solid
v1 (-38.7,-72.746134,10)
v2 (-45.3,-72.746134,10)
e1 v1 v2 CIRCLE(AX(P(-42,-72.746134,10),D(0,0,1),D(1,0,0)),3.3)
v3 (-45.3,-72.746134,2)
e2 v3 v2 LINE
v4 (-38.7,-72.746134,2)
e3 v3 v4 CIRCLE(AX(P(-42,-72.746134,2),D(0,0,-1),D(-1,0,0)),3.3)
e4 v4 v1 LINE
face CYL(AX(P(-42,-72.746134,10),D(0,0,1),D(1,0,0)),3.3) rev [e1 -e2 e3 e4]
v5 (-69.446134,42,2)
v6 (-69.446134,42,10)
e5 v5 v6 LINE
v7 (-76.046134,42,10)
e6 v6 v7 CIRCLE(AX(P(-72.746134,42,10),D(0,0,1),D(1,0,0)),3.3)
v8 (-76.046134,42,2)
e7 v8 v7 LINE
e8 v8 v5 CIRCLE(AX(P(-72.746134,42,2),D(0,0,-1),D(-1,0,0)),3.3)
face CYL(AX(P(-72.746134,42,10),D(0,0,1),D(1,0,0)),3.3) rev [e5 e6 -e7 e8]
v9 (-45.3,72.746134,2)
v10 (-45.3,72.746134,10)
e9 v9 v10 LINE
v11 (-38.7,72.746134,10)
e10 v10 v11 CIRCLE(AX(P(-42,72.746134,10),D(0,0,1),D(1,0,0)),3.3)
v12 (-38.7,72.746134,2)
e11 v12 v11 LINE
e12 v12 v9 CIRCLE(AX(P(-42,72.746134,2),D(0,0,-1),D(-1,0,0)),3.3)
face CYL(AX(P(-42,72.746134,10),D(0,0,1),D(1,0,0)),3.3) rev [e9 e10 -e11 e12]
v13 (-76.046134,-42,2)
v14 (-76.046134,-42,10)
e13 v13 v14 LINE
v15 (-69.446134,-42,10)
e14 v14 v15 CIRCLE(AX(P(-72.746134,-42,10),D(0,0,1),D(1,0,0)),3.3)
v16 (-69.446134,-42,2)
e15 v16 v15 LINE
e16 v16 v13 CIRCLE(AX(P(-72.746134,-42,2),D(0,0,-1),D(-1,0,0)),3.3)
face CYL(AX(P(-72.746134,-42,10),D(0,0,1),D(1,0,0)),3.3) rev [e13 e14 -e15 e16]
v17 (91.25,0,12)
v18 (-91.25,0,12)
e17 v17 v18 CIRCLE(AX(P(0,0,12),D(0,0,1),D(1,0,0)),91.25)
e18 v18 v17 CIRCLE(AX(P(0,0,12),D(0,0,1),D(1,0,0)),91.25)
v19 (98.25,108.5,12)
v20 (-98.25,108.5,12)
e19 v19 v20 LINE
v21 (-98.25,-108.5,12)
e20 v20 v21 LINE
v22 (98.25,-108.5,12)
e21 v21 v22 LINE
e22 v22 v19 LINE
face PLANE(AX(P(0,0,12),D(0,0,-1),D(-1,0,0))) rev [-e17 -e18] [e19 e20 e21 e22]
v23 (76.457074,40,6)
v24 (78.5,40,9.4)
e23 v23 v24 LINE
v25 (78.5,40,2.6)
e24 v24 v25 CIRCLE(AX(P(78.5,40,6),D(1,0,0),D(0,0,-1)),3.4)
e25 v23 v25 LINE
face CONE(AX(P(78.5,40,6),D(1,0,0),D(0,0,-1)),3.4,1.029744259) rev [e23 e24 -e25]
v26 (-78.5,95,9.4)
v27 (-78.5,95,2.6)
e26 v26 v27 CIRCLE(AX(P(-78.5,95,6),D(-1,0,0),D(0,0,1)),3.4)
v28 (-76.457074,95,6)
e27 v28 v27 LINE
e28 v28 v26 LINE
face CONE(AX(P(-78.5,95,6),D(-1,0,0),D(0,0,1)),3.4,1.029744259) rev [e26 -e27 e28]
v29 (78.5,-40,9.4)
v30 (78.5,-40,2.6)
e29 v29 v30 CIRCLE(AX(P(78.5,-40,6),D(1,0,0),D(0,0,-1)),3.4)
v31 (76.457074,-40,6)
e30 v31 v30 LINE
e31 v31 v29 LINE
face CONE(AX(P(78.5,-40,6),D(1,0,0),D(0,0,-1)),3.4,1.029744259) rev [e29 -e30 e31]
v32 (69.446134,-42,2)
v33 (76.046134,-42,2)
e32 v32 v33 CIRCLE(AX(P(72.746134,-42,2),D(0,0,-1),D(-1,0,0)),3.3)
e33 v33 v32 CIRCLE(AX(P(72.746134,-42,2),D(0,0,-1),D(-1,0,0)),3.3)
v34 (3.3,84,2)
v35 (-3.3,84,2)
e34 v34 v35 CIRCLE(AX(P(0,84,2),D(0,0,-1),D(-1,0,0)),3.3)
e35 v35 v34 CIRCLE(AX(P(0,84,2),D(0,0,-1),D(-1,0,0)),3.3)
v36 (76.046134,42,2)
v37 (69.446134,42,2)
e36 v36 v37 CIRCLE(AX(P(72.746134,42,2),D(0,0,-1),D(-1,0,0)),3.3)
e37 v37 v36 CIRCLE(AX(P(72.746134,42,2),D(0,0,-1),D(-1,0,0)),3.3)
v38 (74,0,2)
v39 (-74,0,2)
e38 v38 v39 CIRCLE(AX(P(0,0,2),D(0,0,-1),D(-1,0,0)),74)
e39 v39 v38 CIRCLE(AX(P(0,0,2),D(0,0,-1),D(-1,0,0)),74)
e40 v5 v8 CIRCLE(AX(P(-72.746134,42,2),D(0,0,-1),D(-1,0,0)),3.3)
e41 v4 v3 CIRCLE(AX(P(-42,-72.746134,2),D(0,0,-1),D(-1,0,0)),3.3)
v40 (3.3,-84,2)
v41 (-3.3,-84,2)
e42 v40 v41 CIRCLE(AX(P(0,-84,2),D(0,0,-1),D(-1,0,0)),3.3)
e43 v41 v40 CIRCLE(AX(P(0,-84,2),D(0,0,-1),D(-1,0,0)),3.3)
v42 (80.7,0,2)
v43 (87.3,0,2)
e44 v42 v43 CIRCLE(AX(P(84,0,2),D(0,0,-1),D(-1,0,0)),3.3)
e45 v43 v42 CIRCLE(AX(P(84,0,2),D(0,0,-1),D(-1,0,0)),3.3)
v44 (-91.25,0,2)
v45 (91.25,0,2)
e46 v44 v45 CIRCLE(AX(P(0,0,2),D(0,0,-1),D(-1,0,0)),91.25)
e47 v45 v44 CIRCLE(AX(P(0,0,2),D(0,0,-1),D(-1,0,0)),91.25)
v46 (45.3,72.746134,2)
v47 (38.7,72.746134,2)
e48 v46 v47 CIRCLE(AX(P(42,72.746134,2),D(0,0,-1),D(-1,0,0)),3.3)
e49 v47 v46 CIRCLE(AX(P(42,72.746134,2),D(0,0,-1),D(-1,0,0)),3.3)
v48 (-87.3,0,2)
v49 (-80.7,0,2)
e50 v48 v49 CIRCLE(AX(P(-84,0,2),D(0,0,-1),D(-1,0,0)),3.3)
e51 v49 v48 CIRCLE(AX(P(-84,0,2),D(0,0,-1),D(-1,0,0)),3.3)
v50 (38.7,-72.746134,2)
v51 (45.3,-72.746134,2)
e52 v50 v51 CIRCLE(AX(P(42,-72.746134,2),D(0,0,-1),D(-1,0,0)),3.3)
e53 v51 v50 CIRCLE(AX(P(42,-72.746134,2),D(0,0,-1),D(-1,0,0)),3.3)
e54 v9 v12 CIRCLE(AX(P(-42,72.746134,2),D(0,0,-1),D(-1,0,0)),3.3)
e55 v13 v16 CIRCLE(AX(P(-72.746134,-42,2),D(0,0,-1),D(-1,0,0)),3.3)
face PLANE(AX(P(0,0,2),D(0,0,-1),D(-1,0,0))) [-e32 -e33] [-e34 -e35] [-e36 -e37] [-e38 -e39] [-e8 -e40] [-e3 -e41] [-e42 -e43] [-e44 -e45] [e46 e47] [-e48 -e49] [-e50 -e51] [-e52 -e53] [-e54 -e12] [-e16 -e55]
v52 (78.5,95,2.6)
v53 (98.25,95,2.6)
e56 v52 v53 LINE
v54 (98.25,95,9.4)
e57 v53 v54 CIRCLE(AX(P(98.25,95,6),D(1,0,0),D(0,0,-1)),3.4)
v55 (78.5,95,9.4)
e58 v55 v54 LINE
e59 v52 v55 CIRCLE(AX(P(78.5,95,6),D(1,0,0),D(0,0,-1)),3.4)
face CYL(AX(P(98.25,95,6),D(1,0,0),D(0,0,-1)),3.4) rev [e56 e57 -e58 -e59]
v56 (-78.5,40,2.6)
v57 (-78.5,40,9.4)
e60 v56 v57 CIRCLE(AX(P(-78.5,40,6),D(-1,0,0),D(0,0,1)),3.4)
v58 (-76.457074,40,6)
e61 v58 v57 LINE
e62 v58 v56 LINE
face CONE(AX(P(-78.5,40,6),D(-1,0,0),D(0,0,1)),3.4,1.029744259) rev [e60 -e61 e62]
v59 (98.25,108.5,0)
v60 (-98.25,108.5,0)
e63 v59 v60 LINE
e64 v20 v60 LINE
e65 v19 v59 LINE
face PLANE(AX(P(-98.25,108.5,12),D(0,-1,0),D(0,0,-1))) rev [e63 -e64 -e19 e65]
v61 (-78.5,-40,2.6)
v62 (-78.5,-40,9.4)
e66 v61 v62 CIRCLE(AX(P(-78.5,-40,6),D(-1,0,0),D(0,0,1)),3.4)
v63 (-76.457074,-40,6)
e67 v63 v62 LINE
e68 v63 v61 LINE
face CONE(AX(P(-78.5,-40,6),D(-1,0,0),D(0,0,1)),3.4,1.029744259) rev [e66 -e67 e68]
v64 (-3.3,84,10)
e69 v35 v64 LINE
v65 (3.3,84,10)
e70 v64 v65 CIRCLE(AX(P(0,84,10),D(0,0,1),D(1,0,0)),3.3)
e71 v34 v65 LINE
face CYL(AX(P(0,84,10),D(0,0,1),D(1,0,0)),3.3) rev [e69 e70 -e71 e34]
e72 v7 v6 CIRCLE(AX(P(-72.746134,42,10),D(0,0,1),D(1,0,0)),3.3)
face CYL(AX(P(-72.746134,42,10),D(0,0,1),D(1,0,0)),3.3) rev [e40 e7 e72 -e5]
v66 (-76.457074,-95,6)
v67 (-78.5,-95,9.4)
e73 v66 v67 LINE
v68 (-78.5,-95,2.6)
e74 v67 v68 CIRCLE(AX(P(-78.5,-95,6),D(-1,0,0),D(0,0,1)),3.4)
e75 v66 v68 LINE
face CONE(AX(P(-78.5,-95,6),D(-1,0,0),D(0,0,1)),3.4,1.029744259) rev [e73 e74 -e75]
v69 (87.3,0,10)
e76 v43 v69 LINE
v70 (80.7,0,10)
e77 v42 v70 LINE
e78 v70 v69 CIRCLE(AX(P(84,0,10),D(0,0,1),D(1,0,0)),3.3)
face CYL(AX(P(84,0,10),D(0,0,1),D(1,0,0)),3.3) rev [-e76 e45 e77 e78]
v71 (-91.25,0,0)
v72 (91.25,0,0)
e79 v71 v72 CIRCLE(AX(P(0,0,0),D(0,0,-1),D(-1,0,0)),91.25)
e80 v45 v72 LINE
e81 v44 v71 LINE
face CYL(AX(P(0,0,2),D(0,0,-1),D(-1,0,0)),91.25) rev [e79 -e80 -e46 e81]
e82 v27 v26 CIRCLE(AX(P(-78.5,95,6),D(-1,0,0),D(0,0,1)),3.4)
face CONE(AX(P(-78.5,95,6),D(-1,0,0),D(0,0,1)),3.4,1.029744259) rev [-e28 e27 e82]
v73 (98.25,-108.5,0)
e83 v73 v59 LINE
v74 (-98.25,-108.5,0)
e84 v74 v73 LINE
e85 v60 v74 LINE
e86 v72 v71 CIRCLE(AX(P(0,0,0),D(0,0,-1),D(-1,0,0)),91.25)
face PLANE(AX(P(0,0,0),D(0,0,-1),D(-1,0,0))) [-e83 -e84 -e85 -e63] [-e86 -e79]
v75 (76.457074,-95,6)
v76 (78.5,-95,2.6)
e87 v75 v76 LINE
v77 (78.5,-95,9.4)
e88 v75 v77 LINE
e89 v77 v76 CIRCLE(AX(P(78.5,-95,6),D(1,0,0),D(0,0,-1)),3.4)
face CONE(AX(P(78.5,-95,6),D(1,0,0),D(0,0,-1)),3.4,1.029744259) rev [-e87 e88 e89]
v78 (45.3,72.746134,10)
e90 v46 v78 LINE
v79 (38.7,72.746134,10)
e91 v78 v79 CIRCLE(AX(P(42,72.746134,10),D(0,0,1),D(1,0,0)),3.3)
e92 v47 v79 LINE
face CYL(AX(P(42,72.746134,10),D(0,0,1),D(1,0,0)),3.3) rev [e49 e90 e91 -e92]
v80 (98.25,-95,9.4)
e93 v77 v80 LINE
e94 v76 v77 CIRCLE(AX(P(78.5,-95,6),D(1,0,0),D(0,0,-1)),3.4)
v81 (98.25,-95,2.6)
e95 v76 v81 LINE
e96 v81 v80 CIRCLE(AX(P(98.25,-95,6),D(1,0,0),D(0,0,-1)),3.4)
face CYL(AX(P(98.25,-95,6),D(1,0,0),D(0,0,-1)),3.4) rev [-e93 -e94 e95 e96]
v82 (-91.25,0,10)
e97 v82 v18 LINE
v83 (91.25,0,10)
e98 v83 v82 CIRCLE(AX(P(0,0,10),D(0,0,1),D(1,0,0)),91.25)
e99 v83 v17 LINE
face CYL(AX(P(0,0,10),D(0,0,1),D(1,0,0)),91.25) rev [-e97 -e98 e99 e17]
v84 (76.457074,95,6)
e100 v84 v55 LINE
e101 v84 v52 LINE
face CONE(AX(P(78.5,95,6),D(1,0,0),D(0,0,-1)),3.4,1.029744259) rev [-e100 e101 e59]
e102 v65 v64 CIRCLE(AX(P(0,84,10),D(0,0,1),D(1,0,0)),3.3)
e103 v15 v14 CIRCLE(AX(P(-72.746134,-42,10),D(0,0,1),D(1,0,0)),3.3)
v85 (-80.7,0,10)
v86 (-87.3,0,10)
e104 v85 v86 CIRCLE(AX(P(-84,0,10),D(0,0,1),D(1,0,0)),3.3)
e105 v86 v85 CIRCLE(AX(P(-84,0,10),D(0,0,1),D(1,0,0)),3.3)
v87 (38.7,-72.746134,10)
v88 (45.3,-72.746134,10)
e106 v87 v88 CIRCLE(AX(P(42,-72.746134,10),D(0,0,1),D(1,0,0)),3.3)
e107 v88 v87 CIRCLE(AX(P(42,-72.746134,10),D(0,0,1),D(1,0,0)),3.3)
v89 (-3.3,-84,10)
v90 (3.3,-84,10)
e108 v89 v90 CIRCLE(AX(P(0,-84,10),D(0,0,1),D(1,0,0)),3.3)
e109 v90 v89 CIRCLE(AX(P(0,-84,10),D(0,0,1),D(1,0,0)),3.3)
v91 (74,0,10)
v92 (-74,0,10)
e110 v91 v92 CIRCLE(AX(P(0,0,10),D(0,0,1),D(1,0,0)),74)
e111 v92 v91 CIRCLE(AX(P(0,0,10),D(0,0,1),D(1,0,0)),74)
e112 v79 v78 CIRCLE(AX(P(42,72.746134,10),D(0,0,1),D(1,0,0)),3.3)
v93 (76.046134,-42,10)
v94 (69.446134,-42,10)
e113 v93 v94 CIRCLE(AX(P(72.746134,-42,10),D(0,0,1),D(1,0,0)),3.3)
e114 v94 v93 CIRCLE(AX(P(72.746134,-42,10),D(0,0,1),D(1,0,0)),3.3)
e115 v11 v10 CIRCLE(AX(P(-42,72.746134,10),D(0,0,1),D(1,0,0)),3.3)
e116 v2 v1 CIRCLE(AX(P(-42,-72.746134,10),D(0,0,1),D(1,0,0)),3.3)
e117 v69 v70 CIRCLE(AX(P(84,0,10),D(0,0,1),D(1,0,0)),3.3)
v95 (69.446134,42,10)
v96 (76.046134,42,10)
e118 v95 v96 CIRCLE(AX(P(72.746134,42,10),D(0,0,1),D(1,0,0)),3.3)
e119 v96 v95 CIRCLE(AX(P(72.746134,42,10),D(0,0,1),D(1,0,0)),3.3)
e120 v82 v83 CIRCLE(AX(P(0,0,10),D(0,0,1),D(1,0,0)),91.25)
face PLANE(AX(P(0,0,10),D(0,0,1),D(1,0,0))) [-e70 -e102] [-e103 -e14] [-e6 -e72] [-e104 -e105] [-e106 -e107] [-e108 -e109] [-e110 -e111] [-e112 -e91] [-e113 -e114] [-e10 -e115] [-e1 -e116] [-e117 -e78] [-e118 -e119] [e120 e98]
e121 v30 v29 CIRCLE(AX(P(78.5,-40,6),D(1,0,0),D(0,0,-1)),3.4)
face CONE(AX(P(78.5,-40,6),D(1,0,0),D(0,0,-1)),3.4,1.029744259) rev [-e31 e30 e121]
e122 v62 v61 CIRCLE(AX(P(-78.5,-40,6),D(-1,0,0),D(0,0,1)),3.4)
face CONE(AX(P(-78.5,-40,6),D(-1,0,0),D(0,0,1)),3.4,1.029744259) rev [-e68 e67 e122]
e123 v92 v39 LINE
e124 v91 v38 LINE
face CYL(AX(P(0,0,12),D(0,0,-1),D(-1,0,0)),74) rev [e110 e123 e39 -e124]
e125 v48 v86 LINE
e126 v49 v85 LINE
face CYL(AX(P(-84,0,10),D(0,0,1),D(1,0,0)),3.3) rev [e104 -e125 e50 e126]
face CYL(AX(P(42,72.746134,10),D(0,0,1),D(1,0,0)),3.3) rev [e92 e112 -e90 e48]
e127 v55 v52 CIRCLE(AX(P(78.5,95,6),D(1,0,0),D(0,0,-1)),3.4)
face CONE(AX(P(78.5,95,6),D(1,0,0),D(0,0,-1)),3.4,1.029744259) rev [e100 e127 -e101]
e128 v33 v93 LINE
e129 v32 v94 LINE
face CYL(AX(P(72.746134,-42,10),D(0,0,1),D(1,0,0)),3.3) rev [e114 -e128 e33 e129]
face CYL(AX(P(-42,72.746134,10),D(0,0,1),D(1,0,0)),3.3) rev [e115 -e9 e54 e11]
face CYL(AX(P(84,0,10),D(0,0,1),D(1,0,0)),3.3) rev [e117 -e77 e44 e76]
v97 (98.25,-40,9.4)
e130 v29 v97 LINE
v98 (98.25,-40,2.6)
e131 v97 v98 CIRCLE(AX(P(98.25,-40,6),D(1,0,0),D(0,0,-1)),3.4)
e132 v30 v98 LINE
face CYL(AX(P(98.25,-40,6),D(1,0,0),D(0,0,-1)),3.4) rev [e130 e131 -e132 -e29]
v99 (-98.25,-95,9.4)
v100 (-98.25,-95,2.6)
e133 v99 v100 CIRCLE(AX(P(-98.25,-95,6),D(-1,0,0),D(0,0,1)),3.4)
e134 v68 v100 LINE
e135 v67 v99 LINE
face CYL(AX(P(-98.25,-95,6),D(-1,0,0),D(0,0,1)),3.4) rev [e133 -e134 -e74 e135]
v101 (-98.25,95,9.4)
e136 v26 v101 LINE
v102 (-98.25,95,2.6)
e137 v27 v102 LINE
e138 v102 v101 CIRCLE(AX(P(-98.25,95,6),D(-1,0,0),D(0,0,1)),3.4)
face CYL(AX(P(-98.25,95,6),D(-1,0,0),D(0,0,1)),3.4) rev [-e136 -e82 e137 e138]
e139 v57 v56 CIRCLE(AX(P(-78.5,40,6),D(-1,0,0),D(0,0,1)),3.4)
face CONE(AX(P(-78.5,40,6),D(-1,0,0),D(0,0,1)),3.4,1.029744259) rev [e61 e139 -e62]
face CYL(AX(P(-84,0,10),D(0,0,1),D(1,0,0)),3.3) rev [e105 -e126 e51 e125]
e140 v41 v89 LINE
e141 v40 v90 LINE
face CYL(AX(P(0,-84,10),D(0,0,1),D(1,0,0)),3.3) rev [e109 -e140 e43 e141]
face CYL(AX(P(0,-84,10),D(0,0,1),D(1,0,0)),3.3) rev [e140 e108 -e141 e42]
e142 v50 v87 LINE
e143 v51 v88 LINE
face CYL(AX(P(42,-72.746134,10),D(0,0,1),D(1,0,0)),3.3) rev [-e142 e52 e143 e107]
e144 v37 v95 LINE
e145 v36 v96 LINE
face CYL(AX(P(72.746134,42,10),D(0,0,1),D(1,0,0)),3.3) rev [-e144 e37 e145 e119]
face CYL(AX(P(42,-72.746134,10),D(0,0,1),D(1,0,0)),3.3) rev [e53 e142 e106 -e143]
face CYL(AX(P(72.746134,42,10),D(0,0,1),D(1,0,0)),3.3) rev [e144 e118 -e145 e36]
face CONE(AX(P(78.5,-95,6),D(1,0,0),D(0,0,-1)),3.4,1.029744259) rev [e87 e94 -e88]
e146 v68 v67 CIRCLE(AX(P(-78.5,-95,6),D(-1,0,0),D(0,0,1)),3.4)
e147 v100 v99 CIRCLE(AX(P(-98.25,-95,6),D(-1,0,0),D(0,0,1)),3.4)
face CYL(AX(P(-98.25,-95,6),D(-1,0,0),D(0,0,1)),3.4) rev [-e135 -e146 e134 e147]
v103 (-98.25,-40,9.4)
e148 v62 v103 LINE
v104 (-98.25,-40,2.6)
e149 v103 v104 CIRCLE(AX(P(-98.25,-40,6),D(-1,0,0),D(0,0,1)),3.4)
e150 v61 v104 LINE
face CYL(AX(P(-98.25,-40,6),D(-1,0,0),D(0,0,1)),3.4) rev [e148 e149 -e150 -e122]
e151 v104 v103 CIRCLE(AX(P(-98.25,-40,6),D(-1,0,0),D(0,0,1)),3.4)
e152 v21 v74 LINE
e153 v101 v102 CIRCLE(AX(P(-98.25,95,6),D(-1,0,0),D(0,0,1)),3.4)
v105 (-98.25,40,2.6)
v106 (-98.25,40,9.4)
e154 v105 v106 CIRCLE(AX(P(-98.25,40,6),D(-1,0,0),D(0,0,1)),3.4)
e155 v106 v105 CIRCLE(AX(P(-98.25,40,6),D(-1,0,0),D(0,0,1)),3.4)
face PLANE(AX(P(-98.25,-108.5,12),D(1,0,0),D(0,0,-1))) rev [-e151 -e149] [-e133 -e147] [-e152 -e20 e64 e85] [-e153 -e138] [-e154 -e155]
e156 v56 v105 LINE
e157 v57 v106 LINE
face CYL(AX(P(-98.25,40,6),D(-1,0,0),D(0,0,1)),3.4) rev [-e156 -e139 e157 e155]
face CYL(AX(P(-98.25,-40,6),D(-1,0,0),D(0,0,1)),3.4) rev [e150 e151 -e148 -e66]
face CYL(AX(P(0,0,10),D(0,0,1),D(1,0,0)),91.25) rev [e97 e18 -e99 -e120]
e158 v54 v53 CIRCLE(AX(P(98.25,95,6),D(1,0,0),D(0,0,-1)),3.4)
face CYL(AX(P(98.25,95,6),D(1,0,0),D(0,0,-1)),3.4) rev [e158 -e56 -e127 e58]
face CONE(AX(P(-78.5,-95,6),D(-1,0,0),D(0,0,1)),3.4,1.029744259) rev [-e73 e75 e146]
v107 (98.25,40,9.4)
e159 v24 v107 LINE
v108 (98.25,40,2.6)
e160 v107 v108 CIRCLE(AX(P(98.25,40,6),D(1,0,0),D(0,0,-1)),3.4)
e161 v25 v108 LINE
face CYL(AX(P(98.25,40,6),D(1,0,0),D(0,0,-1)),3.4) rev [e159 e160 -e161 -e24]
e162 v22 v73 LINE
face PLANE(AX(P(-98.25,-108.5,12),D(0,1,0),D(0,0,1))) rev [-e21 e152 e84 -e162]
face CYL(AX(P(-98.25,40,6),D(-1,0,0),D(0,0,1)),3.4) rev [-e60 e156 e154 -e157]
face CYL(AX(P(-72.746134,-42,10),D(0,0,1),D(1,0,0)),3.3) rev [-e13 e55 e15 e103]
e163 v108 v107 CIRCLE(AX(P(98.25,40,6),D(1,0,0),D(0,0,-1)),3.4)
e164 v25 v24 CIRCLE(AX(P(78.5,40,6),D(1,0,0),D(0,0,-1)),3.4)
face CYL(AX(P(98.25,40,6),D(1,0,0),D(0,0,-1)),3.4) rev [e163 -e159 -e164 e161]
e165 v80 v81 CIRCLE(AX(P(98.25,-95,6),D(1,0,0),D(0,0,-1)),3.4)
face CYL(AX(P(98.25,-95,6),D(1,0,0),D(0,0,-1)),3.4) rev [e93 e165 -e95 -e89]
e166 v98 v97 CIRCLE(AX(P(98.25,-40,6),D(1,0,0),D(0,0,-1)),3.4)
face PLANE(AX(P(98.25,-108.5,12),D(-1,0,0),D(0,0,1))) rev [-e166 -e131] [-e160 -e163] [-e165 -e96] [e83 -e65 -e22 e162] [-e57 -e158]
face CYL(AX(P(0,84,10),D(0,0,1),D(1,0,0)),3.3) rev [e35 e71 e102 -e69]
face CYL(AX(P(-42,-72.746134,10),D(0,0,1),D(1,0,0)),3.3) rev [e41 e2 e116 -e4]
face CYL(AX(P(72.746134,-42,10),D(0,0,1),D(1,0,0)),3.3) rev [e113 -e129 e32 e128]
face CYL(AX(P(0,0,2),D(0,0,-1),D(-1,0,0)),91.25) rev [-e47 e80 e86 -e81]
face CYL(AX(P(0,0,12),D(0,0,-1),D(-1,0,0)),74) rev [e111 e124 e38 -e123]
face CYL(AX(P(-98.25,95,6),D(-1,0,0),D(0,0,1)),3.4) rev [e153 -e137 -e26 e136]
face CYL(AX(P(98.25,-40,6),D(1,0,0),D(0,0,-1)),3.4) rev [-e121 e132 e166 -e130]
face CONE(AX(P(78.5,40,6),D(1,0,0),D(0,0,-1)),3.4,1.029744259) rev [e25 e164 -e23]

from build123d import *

# Parameters (mm, degrees)
SKETCH_1_W             = 196.5
SKETCH_1_H             = 217
SKETCH_1_R             = 74
EXTRUDE_1_DEPTH        = 12
SKETCH_2_R             = 91.25
CUT_EXTRUDE_1_DEPTH    = 2
CUT_EXTRUDE_START      = -2
SKETCH_3_R             = 91.25
CUT_EXTRUDE_2_DEPTH    = 2
HOLE_WIZARD_M6_1_D     = 6.6
HOLE_WIZARD_M8_1_D     = 6.8
HOLE_WIZARD_M8_1_DEPTH = 19.75
HOLE_WIZARD_M8_1_TIP   = 2.042926105
HOLE_WIZARD_M8_2_D     = 6.8
HOLE_WIZARD_M8_2_DEPTH = 19.75
HOLE_WIZARD_M8_2_TIP   = 2.042926105


with BuildPart() as part:
    # 草图1 → 凸台-拉伸1 (new body)
    with BuildSketch(Plane.XY):
        Rectangle(SKETCH_1_W, SKETCH_1_H)
        Circle(SKETCH_1_R, mode=Mode.SUBTRACT)
    extrude(amount=EXTRUDE_1_DEPTH)

    # 草图2 → 切除-拉伸1 (cut)
    with BuildSketch(Plane(origin=(0, 0, 0), x_dir=(-1, 0, 0), z_dir=(0, 0, -1))):
        Circle(SKETCH_2_R)
    extrude(amount=-CUT_EXTRUDE_1_DEPTH, mode=Mode.SUBTRACT)

    # 草图3 → 切除-拉伸2 (cut)
    with BuildSketch(Plane.XY.offset(12).offset(CUT_EXTRUDE_START)):
        with Locations(Location((0, 0, 0), (0, 0, 180))):
            Circle(SKETCH_3_R)
    extrude(amount=CUT_EXTRUDE_2_DEPTH, mode=Mode.SUBTRACT)

    # M6 间隙孔1 (through all)
    with Locations(Plane.XY.offset(10)):
        with Locations((0, 84), (42, 72.746133918), (72.746133918, 42), (84, 0), (72.746133918, -42), (42, -72.746133918), (0, -84), (-42, -72.746133918), (-72.746133918, -42), (-84, 0), (-72.746133918, 42), (-42, 72.746133918)):
            Hole(HOLE_WIZARD_M6_1_D / 2)

    # M8 螺纹孔1
    with Locations(Plane.ZY.offset(98.25)):
        with Locations((6, 95), (6, 40), (6, -40), (6, -95)):
            Hole(HOLE_WIZARD_M8_1_D / 2, depth=HOLE_WIZARD_M8_1_DEPTH)
            with Locations((0, 0, -(HOLE_WIZARD_M8_1_DEPTH + HOLE_WIZARD_M8_1_TIP / 2))):  # 118° drill point
                Cone(0, HOLE_WIZARD_M8_1_D / 2, HOLE_WIZARD_M8_1_TIP, mode=Mode.SUBTRACT)

    # M8 螺纹孔2
    with Locations(Plane(origin=(98.25, 0, 0), x_dir=(0, 0, -1), z_dir=(1, 0, 0))):
        with Locations((-6, 95), (-6, 40), (-6, -40), (-6, -95)):
            Hole(HOLE_WIZARD_M8_2_D / 2, depth=HOLE_WIZARD_M8_2_DEPTH)
            with Locations((0, 0, -(HOLE_WIZARD_M8_2_DEPTH + HOLE_WIZARD_M8_2_TIP / 2))):  # 118° drill point
                Cone(0, HOLE_WIZARD_M8_2_D / 2, HOLE_WIZARD_M8_2_TIP, mode=Mode.SUBTRACT)


solid = part.part
